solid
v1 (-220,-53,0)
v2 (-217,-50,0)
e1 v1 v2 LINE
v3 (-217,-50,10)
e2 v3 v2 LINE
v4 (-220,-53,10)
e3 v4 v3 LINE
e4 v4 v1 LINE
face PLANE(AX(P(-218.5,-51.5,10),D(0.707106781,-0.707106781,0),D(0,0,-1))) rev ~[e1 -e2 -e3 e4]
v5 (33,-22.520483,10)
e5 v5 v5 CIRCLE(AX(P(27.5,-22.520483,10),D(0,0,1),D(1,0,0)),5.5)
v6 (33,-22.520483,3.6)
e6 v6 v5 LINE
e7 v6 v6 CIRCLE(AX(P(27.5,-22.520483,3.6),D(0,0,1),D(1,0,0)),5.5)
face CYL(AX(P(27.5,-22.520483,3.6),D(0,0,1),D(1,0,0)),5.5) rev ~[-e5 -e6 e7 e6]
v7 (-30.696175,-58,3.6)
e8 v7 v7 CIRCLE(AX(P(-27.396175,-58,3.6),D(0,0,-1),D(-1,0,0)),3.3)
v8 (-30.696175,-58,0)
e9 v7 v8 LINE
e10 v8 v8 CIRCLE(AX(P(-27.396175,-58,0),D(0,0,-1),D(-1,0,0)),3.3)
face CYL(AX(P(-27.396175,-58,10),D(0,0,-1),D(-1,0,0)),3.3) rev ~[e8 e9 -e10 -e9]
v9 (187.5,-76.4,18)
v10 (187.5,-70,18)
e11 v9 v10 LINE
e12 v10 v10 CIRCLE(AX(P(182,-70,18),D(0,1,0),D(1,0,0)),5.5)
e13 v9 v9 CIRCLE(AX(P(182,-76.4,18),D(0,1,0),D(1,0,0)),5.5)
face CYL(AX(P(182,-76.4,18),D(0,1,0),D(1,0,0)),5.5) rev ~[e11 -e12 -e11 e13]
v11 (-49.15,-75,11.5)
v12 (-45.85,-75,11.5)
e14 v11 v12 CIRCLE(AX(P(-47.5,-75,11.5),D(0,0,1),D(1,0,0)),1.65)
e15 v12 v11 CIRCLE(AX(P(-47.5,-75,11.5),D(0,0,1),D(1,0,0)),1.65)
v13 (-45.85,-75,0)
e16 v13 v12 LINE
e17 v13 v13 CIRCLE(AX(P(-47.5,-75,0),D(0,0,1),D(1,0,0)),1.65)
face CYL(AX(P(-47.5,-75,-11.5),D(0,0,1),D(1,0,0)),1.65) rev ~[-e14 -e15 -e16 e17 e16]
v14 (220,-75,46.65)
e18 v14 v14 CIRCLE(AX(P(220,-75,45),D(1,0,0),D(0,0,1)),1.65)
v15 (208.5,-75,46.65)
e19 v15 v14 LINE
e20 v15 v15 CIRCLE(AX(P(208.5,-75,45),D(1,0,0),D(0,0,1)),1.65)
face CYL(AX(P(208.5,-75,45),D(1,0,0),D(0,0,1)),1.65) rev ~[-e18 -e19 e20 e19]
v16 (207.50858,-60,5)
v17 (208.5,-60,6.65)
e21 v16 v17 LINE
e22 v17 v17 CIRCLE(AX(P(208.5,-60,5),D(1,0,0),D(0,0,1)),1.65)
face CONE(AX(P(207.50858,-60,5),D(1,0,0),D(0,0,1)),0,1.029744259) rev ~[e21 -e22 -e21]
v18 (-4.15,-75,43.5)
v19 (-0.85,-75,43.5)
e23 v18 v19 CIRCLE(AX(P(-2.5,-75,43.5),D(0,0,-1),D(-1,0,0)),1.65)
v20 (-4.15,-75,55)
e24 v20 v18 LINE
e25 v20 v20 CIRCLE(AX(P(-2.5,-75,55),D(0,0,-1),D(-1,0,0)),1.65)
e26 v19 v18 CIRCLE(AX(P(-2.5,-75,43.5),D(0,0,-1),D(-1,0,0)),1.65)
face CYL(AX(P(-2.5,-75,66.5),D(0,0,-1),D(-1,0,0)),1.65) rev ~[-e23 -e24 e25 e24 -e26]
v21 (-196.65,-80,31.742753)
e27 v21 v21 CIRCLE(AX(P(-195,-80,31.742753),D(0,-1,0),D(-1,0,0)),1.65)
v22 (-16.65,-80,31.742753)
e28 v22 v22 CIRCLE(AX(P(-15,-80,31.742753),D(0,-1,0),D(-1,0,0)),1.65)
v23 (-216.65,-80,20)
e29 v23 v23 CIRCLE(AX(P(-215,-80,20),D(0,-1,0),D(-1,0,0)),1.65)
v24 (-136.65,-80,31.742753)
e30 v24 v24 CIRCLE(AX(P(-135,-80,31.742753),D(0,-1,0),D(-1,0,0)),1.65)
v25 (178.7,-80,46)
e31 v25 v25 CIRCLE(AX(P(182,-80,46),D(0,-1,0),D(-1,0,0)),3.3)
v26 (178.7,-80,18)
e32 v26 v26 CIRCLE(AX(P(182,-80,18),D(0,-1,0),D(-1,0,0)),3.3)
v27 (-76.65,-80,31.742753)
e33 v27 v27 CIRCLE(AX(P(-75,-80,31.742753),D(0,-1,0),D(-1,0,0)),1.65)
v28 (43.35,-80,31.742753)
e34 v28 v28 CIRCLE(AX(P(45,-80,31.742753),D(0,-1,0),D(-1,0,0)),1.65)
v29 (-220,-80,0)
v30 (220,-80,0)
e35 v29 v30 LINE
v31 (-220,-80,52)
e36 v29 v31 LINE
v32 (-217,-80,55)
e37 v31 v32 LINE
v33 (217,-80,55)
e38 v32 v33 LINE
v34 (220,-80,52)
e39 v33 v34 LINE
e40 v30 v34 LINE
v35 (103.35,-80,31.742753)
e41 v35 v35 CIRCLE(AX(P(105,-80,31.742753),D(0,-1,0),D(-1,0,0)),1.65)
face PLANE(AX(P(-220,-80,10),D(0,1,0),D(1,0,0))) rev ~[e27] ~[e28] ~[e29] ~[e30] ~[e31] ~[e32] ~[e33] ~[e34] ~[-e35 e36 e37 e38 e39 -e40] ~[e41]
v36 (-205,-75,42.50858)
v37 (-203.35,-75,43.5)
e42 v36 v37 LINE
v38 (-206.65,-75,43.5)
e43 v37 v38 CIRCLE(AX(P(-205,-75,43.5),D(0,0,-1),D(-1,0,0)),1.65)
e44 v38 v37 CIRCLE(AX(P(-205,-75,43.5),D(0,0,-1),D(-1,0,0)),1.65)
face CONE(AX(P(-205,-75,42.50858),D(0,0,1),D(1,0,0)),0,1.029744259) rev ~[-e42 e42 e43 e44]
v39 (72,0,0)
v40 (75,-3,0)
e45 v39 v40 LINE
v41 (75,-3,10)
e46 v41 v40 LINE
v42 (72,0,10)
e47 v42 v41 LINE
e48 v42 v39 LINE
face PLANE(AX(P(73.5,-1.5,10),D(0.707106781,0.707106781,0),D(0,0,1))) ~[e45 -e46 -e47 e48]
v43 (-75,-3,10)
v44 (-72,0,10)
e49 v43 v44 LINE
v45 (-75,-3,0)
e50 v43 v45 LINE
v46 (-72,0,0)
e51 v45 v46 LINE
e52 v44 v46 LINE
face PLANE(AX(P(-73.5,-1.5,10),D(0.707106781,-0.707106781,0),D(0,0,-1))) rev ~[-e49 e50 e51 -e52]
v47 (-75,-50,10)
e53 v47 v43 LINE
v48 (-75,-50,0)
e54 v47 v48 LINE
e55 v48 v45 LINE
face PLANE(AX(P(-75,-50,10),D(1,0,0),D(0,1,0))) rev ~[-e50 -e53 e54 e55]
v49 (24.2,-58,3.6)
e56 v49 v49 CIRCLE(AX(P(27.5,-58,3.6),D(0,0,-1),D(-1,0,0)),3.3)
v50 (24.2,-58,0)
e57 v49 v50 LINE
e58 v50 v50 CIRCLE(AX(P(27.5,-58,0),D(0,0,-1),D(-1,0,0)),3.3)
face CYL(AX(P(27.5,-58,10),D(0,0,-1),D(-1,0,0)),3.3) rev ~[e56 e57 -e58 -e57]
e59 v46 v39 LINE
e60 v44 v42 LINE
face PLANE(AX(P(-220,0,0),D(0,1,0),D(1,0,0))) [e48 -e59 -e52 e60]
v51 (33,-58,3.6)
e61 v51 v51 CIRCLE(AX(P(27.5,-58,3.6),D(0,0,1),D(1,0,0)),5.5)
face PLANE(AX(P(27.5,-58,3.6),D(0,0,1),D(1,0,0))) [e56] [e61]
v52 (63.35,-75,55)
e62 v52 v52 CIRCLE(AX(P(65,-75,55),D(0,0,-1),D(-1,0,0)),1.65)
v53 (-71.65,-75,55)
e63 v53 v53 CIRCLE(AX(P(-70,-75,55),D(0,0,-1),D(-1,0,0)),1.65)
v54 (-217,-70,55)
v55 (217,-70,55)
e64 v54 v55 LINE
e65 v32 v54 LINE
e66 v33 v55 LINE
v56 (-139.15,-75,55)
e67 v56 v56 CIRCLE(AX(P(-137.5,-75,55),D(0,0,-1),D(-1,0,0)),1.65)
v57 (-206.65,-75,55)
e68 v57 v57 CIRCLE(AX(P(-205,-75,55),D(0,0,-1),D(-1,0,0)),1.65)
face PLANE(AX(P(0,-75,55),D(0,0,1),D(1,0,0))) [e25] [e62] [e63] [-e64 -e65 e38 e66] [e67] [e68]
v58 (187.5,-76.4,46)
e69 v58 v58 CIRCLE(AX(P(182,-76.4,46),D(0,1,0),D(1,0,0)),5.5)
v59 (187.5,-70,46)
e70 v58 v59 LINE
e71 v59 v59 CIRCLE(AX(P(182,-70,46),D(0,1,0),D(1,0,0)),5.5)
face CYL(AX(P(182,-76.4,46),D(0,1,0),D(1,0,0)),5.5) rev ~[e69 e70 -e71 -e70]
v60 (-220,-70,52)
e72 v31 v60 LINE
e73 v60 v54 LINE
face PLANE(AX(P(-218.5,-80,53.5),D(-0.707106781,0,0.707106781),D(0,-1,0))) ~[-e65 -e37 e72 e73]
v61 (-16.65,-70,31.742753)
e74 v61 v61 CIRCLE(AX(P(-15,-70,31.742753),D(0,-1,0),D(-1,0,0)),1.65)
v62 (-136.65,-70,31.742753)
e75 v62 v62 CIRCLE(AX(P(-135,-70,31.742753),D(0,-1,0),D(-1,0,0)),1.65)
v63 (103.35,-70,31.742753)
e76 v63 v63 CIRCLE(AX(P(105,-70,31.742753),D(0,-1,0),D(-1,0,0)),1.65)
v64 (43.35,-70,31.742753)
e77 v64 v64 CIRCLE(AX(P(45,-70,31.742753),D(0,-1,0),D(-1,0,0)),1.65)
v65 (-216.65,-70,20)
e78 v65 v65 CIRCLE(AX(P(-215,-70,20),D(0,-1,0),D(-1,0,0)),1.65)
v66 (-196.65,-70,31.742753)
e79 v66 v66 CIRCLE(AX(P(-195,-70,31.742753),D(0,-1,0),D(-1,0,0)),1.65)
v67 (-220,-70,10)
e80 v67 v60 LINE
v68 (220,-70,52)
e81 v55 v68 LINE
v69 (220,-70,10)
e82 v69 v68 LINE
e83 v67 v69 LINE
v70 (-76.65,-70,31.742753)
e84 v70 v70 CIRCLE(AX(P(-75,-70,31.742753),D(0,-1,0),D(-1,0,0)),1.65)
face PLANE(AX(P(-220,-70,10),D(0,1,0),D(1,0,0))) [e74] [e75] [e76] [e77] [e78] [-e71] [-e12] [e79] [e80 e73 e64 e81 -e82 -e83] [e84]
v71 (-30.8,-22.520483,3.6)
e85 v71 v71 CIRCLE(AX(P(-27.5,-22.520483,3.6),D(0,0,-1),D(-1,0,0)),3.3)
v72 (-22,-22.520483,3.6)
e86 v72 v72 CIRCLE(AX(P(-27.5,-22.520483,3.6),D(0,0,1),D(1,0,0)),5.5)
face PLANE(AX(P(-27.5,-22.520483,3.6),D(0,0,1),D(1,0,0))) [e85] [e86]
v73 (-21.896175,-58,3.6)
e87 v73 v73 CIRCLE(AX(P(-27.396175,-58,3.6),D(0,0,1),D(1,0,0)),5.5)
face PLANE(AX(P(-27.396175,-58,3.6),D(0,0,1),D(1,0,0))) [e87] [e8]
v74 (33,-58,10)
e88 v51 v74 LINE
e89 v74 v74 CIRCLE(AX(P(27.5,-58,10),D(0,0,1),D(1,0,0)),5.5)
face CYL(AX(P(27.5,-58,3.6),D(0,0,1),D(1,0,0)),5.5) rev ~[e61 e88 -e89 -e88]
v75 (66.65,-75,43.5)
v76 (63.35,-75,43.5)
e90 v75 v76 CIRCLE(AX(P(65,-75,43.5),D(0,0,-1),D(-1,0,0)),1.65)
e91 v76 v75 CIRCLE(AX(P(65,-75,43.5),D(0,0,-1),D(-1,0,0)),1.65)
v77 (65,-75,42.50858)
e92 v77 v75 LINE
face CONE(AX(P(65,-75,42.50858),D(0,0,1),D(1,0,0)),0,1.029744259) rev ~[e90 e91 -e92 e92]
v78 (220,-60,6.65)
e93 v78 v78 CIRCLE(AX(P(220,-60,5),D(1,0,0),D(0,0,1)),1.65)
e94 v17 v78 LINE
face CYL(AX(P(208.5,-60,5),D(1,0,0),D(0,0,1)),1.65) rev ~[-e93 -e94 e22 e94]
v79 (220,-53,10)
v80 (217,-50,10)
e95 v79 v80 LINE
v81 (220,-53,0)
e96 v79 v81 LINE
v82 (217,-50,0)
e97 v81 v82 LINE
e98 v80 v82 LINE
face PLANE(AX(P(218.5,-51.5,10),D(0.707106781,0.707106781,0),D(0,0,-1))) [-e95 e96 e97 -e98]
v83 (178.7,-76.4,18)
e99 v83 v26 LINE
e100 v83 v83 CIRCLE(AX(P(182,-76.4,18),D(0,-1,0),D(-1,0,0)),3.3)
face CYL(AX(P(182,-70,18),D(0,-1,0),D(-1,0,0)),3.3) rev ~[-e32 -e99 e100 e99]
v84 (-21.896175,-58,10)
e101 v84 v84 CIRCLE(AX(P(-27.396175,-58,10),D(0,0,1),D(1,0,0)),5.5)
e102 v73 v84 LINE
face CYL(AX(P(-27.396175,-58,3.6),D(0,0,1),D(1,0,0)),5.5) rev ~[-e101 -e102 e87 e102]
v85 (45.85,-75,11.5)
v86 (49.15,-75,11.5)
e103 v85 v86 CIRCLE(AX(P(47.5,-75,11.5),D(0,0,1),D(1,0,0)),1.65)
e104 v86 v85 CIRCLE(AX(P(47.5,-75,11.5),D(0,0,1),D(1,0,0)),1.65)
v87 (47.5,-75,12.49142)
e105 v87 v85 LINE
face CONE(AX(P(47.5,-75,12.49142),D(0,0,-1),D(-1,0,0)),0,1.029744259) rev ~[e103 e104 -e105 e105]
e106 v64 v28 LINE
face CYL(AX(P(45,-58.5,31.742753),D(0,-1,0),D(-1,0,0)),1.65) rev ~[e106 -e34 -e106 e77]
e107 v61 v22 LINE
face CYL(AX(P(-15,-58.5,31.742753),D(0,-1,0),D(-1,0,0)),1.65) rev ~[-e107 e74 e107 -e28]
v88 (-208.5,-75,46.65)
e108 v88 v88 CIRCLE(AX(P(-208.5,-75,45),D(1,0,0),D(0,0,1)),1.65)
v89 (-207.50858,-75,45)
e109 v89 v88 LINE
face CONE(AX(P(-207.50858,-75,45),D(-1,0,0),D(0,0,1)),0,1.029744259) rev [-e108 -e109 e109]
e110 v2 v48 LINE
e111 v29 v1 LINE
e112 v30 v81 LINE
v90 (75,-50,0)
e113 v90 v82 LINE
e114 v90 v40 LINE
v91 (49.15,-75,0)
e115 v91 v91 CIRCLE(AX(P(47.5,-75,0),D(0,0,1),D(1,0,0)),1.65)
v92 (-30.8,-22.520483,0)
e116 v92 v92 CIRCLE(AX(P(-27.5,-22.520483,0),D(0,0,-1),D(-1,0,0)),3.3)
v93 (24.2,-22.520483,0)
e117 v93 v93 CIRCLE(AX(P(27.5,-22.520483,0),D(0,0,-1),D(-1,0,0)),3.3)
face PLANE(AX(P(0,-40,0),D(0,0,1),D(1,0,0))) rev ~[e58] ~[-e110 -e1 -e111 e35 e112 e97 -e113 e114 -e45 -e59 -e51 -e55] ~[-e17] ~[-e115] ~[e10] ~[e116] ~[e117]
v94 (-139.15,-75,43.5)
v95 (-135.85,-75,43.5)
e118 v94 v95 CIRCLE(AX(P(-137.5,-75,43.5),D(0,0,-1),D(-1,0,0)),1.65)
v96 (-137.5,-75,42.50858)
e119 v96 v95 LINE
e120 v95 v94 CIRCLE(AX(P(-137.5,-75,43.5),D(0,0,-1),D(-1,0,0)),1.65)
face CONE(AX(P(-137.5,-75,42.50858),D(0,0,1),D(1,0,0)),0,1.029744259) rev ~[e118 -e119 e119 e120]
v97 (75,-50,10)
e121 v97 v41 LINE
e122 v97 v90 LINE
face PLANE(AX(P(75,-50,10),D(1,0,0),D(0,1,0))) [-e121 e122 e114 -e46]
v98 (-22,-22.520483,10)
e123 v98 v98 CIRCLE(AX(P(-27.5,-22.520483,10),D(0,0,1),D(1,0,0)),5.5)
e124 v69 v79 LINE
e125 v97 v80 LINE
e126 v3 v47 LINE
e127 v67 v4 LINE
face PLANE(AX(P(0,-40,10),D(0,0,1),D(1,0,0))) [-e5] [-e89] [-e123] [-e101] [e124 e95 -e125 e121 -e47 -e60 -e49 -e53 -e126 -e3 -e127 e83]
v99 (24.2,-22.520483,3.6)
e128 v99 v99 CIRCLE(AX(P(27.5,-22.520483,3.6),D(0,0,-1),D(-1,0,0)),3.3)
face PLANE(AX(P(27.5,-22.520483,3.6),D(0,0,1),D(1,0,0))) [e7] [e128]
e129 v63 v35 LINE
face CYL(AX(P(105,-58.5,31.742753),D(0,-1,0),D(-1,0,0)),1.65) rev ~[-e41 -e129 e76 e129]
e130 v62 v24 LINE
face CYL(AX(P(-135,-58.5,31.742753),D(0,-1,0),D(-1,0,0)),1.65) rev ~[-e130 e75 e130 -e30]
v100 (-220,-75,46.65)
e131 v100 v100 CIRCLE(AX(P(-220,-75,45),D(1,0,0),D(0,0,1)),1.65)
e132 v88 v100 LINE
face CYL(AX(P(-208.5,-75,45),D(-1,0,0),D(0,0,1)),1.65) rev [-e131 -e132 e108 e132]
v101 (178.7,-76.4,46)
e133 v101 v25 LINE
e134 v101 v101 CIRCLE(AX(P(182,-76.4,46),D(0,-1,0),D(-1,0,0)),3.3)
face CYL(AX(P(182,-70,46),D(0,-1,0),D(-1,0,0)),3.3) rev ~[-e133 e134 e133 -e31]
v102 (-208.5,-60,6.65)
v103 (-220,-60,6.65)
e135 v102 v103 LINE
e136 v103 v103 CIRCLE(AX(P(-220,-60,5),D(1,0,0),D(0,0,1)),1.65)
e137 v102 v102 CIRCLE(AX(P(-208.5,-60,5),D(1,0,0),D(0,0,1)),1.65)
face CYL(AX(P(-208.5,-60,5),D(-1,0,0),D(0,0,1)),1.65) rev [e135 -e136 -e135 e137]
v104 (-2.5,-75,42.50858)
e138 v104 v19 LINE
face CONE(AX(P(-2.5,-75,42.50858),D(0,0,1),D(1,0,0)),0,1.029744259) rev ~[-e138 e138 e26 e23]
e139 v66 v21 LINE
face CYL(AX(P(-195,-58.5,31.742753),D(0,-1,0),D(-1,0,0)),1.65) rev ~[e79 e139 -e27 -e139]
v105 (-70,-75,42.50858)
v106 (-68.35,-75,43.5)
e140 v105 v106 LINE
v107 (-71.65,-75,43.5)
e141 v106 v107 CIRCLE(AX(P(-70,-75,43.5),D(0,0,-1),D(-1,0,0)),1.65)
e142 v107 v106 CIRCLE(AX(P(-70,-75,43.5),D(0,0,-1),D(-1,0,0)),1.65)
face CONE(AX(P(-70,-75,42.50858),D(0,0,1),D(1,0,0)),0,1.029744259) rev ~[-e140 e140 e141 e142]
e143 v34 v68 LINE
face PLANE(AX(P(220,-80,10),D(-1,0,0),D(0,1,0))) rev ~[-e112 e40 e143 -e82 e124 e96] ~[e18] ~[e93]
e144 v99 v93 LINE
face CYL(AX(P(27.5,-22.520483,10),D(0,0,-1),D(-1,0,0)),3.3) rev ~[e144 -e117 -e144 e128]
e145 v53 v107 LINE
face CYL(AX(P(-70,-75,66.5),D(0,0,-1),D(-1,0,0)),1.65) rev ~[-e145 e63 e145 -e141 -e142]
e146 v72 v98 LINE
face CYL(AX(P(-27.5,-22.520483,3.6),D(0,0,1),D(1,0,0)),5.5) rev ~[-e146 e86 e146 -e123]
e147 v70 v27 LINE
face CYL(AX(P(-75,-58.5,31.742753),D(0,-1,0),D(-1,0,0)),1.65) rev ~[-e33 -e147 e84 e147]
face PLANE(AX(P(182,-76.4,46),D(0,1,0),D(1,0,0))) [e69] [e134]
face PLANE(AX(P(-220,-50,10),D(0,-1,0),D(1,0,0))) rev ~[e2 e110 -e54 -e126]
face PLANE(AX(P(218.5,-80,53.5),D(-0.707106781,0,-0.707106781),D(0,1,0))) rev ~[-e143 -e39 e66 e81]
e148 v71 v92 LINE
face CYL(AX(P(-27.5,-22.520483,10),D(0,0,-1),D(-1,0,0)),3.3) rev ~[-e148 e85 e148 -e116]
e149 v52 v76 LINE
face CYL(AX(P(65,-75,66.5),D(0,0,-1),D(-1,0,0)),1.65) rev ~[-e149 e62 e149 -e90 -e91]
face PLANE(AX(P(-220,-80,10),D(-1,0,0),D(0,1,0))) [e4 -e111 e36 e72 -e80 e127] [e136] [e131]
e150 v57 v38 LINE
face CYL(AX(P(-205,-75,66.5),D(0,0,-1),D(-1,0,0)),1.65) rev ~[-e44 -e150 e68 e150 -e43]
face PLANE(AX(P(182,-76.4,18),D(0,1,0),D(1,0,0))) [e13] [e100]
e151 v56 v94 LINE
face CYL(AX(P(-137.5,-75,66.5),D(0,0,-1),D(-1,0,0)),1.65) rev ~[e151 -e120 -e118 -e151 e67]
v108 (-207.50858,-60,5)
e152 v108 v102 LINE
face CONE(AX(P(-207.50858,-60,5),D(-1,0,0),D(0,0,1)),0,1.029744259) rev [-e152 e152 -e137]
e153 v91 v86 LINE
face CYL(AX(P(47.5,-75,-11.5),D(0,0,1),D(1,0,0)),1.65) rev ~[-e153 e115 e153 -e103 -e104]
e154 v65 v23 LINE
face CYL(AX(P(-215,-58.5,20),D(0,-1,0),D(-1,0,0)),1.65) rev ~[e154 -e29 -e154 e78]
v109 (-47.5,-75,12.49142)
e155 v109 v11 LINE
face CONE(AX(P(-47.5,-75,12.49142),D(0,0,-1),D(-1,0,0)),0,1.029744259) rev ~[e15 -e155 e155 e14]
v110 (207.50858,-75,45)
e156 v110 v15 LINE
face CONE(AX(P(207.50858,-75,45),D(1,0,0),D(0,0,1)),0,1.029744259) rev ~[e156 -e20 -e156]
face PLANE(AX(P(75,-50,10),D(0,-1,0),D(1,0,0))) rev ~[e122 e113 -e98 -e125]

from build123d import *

# Parameters (mm, degrees)
SKETCH_2_W                   = 440
SKETCH_2_H                   = 80
EXTRUDE_1_DEPTH              = 10
SKETCH_3_W                   = 440
SKETCH_3_H                   = 10
EXTRUDE_2_DEPTH              = 45
SKETCH_5_W                   = 145
SKETCH_5_H                   = 50
CUT_EXTRUDE_2_DEPTH          = 239.379948821
HOLE_WIZARD_M6_1_D           = 6.6
HOLE_WIZARD_M6_1_DEPTH       = 22.25
HOLE_WIZARD_M6_1_CBORE_D     = 11
HOLE_WIZARD_M6_1_CBORE_DEPTH = 6.4
HOLE_WIZARD_M6_1_TIP         = 1.982840043
HOLE_WIZARD_M4_1_D           = 3.3
HOLE_WIZARD_M4_1_DEPTH       = 11.5
HOLE_WIZARD_M4_1_TIP         = 0.991420021
HOLE_WIZARD_M4_2_D           = 3.3
HOLE_WIZARD_M4_2_DEPTH       = 11.5
HOLE_WIZARD_M4_2_TIP         = 0.991420021
CHAMFER_1_SIZE               = 3
HOLE_WIZARD_M6_2_D           = 6.6
HOLE_WIZARD_M6_2_DEPTH       = 17
HOLE_WIZARD_M6_2_CBORE_D     = 11
HOLE_WIZARD_M6_2_CBORE_DEPTH = 6.4
HOLE_WIZARD_M6_2_TIP         = 1.982840043
HOLE_WIZARD_M4_3_D           = 3.3
HOLE_WIZARD_M4_3_DEPTH       = 11.5
HOLE_WIZARD_M4_3_TIP         = 0.991420021
HOLE_WIZARD_M4_4_AT_2_COUNT  = 2
HOLE_WIZARD_M4_4_AT_2_PITCH  = 42.720018727
HOLE_WIZARD_M4_5_D           = 3.3
HOLE_WIZARD_M4_5_DEPTH       = 11.5
HOLE_WIZARD_M4_5_TIP         = 0.991420021


with BuildPart() as part:
    # 草图2 → 凸台-拉伸1 (new body)
    with BuildSketch(Plane.XY):
        with Locations((0, -40)):
            Rectangle(SKETCH_2_W, SKETCH_2_H)
    extrude(amount=EXTRUDE_1_DEPTH)

    # 草图3 → 凸台-拉伸2 (add)
    with BuildSketch(Plane.XY.offset(10)):
        with Locations((0, -75)):
            Rectangle(SKETCH_3_W, SKETCH_3_H)
    extrude(amount=EXTRUDE_2_DEPTH)

    # 草图5 → 切除-拉伸2 (cut, through all)
    with BuildSketch(Plane.XY.offset(10)):
        with Locations((-147.5, -25)):
            Rectangle(SKETCH_5_W, SKETCH_5_H)
        with Locations((147.5, -25)):
            Rectangle(SKETCH_5_W, SKETCH_5_H)
    extrude(amount=-CUT_EXTRUDE_2_DEPTH, mode=Mode.SUBTRACT)

    # M6 六角凹头螺钉的柱形沉头孔1
    with Locations(Plane.XY.offset(10)):
        with Locations((-27.5, -22.520483068), (27.5, -22.520483068), (27.5, -58), (-27.396175046, -58)):
            CounterBoreHole(HOLE_WIZARD_M6_1_D / 2, HOLE_WIZARD_M6_1_CBORE_D / 2, HOLE_WIZARD_M6_1_CBORE_DEPTH, depth=HOLE_WIZARD_M6_1_DEPTH)
            with Locations((0, 0, -(HOLE_WIZARD_M6_1_DEPTH + HOLE_WIZARD_M6_1_TIP / 2))):  # 118° drill point
                Cone(0, HOLE_WIZARD_M6_1_D / 2, HOLE_WIZARD_M6_1_TIP, mode=Mode.SUBTRACT)

    # M4 螺纹孔1
    with Locations(Plane(origin=(0, -70, 0), x_dir=(1, 0, 0), z_dir=(0, 1, 0))):
        with Locations((-195, -31.742753413), (-135, -31.742753413), (-75, -31.742753413), (-15, -31.742753413), (45, -31.742753413), (105, -31.742753413)):
            Hole(HOLE_WIZARD_M4_1_D / 2, depth=HOLE_WIZARD_M4_1_DEPTH)
            with Locations((0, 0, -(HOLE_WIZARD_M4_1_DEPTH + HOLE_WIZARD_M4_1_TIP / 2))):  # 118° drill point
                Cone(0, HOLE_WIZARD_M4_1_D / 2, HOLE_WIZARD_M4_1_TIP, mode=Mode.SUBTRACT)

    # M4 螺纹孔2
    with Locations(Plane.XY.offset(55)):
        with Locations((-205, -75), (-137.5, -75), (-70, -75), (-2.5, -75), (65, -75)):
            Hole(HOLE_WIZARD_M4_2_D / 2, depth=HOLE_WIZARD_M4_2_DEPTH)
            with Locations((0, 0, -(HOLE_WIZARD_M4_2_DEPTH + HOLE_WIZARD_M4_2_TIP / 2))):  # 118° drill point
                Cone(0, HOLE_WIZARD_M4_2_D / 2, HOLE_WIZARD_M4_2_TIP, mode=Mode.SUBTRACT)

    # 倒角1
    chamfer_1_edges = [part.edges().sort_by_distance(p)[0] for p in [
        (-220, -75, 55),
        (220, -75, 55),
        (-220, -50, 5),
        (-75, 0, 5),
        (75, 0, 5),
        (220, -50, 5),
    ]]
    chamfer(chamfer_1_edges, length=CHAMFER_1_SIZE)

    # M6 六角凹头螺钉的柱形沉头孔2
    with Locations(Plane(origin=(0, -70, 0), x_dir=(1, 0, 0), z_dir=(0, 1, 0))):
        with Locations((182, -18), (182, -46)):
            CounterBoreHole(HOLE_WIZARD_M6_2_D / 2, HOLE_WIZARD_M6_2_CBORE_D / 2, HOLE_WIZARD_M6_2_CBORE_DEPTH, depth=HOLE_WIZARD_M6_2_DEPTH)
            with Locations((0, 0, -(HOLE_WIZARD_M6_2_DEPTH + HOLE_WIZARD_M6_2_TIP / 2))):  # 118° drill point
                Cone(0, HOLE_WIZARD_M6_2_D / 2, HOLE_WIZARD_M6_2_TIP, mode=Mode.SUBTRACT)

    # M4 螺纹孔3
    with Locations(Plane(origin=(0, -70, 0), x_dir=(1, 0, 0), z_dir=(0, 1, 0))):
        with Locations((-215, -20)):
            Hole(HOLE_WIZARD_M4_3_D / 2, depth=HOLE_WIZARD_M4_3_DEPTH)
            with Locations((0, 0, -(HOLE_WIZARD_M4_3_DEPTH + HOLE_WIZARD_M4_3_TIP / 2))):  # 118° drill point
                Cone(0, HOLE_WIZARD_M4_3_D / 2, HOLE_WIZARD_M4_3_TIP, mode=Mode.SUBTRACT)

    # 草图17 → M4 螺纹孔4 (revolve, cut)
    with BuildSketch(Plane(origin=(-220, -75, 45), x_dir=(0, 0, 1), z_dir=(0, 1, 0))):
        Polygon((0, 0), (0, 12.491420021), (1.65, 11.5), (1.65, 0), align=None)
    hole_wizard_m4_4 = revolve(axis=Axis((-226.35, -75, 45), (1, 0, 0)), mode=Mode.SUBTRACT)

    # M4 螺纹孔4 at 2: M4 螺纹孔4 ×2
    with Locations(*[Vector(0, 0.35112344158839187, -0.9363291775690445) * (i * HOLE_WIZARD_M4_4_AT_2_PITCH) for i in range(1, HOLE_WIZARD_M4_4_AT_2_COUNT)]):
        add(hole_wizard_m4_4, mode=Mode.SUBTRACT)

    # 镜向1: M4 螺纹孔4 across plane
    add(hole_wizard_m4_4.mirror(Plane(origin=(0, 0, 0), x_dir=(0, 0, 1), z_dir=(1, 0, 0))), mode=Mode.SUBTRACT)

    # 镜向1 copy 1 sketch → 镜向1 copy 1 (revolve, cut)
    with BuildSketch(Plane(origin=(220, -60, 5), x_dir=(0, 0, 1), z_dir=(0, 1, 0))):
        Polygon((0, 0), (0, -12.491420021), (1.65, -11.5), (1.65, 0), align=None)
    revolve(axis=Axis((226.35, -60, 5), (1, 0, 0)), mode=Mode.SUBTRACT)

    # M4 螺纹孔5
    with Locations(Plane(origin=(0, 0, 0), x_dir=(-1, 0, 0), z_dir=(0, 0, -1))):
        with Locations((-47.5, -75), (47.5, -75)):
            Hole(HOLE_WIZARD_M4_5_D / 2, depth=HOLE_WIZARD_M4_5_DEPTH)
            with Locations((0, 0, -(HOLE_WIZARD_M4_5_DEPTH + HOLE_WIZARD_M4_5_TIP / 2))):  # 118° drill point
                Cone(0, HOLE_WIZARD_M4_5_D / 2, HOLE_WIZARD_M4_5_TIP, mode=Mode.SUBTRACT)


solid = part.part
